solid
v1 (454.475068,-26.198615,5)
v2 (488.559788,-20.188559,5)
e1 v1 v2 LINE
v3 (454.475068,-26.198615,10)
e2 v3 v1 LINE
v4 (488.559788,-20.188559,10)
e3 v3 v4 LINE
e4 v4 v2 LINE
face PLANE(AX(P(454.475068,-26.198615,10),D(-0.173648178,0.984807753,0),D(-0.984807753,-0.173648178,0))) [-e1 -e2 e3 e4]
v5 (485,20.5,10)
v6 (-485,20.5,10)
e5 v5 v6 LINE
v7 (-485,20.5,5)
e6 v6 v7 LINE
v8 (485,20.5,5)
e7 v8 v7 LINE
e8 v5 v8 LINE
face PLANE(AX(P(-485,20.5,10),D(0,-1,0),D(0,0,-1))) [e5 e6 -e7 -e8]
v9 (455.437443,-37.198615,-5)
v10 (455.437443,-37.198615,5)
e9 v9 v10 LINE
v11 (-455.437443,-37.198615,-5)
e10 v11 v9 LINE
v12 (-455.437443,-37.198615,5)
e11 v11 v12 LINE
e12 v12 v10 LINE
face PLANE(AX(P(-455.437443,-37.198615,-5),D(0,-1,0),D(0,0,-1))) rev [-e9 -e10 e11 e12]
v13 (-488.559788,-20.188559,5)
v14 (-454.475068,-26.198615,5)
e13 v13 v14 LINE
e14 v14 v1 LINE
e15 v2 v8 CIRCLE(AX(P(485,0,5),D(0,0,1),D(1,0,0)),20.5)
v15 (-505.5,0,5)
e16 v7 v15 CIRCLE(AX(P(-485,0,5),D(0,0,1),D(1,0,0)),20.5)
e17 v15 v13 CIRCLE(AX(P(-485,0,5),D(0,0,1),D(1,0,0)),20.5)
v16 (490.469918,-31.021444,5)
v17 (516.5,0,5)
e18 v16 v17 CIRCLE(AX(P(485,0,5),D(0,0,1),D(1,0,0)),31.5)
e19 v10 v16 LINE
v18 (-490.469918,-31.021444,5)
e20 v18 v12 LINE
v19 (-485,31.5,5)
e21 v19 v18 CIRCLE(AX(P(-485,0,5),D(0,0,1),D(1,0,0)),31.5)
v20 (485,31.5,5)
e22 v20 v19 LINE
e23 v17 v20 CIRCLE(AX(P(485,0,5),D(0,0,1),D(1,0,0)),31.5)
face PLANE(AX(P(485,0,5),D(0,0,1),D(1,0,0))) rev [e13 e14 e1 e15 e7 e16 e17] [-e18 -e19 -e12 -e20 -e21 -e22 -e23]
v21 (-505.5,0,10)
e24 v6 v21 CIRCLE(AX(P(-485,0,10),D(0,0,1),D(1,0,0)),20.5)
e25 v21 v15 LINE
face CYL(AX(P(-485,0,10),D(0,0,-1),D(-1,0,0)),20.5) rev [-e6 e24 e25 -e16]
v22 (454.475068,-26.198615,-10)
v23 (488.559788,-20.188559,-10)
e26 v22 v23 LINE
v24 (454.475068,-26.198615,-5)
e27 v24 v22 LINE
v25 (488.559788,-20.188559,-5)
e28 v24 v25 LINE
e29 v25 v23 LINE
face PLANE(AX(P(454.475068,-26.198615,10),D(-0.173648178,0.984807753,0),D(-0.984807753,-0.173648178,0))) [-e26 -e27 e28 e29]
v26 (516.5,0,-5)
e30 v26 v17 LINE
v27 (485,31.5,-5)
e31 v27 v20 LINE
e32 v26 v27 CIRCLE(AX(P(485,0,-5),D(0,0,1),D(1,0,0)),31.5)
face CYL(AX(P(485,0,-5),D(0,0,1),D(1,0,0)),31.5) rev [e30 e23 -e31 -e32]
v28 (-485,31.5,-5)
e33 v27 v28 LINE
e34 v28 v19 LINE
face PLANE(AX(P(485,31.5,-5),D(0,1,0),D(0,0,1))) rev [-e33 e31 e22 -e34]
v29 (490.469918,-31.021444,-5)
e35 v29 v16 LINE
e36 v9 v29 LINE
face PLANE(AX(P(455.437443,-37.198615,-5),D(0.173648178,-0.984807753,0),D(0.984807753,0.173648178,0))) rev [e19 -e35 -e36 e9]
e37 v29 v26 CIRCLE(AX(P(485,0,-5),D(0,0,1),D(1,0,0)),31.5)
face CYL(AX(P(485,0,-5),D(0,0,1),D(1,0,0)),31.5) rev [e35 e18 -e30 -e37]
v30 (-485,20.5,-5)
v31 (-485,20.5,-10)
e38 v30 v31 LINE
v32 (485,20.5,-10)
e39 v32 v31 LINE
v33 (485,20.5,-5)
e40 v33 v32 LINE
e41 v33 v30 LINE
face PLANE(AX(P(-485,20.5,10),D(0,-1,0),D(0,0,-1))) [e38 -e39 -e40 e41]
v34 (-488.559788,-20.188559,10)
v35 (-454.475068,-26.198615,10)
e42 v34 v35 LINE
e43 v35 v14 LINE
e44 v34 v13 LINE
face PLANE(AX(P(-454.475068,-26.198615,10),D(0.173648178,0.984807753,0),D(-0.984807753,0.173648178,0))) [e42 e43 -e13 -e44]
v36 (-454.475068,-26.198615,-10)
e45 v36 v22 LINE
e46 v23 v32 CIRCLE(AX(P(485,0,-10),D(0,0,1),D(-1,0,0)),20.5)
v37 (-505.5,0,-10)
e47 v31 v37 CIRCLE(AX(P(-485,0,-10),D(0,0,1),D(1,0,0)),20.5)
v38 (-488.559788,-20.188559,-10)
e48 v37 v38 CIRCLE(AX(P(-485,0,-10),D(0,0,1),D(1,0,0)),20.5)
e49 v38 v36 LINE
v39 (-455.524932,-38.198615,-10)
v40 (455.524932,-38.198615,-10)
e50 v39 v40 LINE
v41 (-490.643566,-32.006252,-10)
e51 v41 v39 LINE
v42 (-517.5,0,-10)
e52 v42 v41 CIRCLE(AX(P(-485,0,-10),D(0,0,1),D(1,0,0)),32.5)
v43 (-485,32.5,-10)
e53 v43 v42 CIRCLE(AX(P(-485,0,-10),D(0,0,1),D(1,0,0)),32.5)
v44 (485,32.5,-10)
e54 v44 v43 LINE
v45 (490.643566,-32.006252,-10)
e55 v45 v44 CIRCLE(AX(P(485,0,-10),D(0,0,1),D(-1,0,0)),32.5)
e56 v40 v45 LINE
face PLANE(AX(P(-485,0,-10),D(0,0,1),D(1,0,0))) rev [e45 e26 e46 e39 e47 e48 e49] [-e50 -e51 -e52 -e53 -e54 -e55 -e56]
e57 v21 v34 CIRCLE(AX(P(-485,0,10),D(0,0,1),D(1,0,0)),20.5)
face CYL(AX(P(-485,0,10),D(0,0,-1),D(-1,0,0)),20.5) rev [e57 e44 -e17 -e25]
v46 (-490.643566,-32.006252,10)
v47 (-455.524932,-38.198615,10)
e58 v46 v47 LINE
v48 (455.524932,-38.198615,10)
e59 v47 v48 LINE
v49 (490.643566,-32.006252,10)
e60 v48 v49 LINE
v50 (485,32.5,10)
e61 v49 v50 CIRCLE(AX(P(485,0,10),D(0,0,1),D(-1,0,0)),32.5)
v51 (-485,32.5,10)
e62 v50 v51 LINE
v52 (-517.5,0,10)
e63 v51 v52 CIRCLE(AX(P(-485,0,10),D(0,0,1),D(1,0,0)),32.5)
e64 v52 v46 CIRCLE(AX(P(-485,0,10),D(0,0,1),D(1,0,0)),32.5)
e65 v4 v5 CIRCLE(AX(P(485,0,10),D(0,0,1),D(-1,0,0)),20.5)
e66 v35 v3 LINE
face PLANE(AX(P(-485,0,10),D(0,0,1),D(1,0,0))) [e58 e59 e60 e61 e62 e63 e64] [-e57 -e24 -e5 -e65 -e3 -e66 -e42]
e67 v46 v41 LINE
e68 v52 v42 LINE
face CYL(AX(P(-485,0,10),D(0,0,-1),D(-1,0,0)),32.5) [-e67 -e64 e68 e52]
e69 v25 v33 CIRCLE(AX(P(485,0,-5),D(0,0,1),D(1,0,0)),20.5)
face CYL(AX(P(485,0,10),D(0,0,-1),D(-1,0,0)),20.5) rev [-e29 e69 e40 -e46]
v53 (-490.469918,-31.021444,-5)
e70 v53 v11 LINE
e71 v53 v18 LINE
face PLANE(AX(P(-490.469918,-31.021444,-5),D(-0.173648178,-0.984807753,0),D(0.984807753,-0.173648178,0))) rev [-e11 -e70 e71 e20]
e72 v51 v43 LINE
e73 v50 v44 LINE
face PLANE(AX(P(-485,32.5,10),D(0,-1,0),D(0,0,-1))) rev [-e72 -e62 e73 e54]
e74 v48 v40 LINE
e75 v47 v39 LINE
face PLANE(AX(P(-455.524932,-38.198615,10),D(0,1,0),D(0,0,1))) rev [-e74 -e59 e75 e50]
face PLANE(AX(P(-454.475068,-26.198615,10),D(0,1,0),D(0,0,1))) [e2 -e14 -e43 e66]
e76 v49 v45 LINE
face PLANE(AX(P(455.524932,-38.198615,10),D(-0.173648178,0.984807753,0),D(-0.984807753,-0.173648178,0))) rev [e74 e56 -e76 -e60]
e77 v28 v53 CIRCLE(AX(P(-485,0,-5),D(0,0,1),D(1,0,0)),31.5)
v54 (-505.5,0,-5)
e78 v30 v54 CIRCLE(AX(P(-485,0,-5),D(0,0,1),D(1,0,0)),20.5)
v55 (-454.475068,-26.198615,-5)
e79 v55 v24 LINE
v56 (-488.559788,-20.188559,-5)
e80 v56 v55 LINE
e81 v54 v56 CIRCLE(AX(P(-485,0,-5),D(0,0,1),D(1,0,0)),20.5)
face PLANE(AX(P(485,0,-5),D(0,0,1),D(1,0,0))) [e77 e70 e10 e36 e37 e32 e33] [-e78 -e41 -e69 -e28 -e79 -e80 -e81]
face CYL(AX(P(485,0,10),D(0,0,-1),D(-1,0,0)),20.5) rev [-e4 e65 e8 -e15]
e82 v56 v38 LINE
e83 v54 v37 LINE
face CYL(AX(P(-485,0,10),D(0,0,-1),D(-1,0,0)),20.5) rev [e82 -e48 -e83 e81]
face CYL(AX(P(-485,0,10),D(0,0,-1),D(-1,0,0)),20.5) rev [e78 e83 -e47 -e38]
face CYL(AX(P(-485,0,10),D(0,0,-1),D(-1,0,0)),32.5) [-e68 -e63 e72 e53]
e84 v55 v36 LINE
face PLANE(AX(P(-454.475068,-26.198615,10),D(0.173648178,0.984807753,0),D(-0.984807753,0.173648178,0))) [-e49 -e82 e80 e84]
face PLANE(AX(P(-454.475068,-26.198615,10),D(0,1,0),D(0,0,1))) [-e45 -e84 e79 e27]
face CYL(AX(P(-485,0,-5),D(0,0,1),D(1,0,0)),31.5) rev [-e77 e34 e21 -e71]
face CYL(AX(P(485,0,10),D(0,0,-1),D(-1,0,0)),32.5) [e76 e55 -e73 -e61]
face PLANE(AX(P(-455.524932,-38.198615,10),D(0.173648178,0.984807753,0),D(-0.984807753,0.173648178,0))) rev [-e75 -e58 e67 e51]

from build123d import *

# Parameters (mm, degrees)
BOSS_EXTRUDE1_DEPTH = 10
CUT_EXTRUDE1_DEPTH  = 5


with BuildPart() as part:
    # Sketch2 → Boss-Extrude1 (new, symmetric)
    with BuildSketch(Plane.XY):
        with BuildLine():
            Line((-485, 32.5), (485, 32.5))
            ThreePointArc((485, 32.5), (517.376327688, 2.832561639), (490.643565774, -32.006251973))
            Line((490.643565774, -32.006251973), (455.524931981, -38.198614636))
            Line((455.524931981, -38.198614636), (-455.524931981, -38.198614636))
            Line((-455.524931981, -38.198614636), (-490.643565774, -32.006251973))
            ThreePointArc((-490.643565774, -32.006251973), (-517.376327688, 2.832561639), (-485, 32.5))
        make_face()
        with BuildLine():
            Line((-485, 20.5), (485, 20.5))
            ThreePointArc((485, 20.5), (505.421991311, 1.786692726), (488.559787642, -20.188558937))
            Line((488.559787642, -20.188558937), (454.475068019, -26.198614636))
            Line((454.475068019, -26.198614636), (-454.475068019, -26.198614636))
            Line((-454.475068019, -26.198614636), (-488.559787642, -20.188558937))
            ThreePointArc((-488.559787642, -20.188558937), (-505.421991311, 1.786692726), (-485, 20.5))
        make_face(mode=Mode.SUBTRACT)
    extrude(amount=BOSS_EXTRUDE1_DEPTH, both=True)

    # Sketch8 → Cut-Extrude1 (cut, symmetric)
    with BuildSketch(Plane.XY):
        with BuildLine():
            Line((455.437443318, -37.198614636), (490.469917597, -31.02144422))
            ThreePointArc((490.469917597, -31.02144422), (516.38013299, 2.745405897), (485, 31.5))
            Line((485, 31.5), (-485, 31.5))
            ThreePointArc((-485, 31.5), (-516.38013299, 2.745405897), (-490.469917597, -31.02144422))
            Line((-490.469917597, -31.02144422), (-455.437443318, -37.198614636))
            Line((-455.437443318, -37.198614636), (455.437443318, -37.198614636))
        make_face()
    extrude(amount=CUT_EXTRUDE1_DEPTH, both=True, mode=Mode.SUBTRACT)


solid = part.part
